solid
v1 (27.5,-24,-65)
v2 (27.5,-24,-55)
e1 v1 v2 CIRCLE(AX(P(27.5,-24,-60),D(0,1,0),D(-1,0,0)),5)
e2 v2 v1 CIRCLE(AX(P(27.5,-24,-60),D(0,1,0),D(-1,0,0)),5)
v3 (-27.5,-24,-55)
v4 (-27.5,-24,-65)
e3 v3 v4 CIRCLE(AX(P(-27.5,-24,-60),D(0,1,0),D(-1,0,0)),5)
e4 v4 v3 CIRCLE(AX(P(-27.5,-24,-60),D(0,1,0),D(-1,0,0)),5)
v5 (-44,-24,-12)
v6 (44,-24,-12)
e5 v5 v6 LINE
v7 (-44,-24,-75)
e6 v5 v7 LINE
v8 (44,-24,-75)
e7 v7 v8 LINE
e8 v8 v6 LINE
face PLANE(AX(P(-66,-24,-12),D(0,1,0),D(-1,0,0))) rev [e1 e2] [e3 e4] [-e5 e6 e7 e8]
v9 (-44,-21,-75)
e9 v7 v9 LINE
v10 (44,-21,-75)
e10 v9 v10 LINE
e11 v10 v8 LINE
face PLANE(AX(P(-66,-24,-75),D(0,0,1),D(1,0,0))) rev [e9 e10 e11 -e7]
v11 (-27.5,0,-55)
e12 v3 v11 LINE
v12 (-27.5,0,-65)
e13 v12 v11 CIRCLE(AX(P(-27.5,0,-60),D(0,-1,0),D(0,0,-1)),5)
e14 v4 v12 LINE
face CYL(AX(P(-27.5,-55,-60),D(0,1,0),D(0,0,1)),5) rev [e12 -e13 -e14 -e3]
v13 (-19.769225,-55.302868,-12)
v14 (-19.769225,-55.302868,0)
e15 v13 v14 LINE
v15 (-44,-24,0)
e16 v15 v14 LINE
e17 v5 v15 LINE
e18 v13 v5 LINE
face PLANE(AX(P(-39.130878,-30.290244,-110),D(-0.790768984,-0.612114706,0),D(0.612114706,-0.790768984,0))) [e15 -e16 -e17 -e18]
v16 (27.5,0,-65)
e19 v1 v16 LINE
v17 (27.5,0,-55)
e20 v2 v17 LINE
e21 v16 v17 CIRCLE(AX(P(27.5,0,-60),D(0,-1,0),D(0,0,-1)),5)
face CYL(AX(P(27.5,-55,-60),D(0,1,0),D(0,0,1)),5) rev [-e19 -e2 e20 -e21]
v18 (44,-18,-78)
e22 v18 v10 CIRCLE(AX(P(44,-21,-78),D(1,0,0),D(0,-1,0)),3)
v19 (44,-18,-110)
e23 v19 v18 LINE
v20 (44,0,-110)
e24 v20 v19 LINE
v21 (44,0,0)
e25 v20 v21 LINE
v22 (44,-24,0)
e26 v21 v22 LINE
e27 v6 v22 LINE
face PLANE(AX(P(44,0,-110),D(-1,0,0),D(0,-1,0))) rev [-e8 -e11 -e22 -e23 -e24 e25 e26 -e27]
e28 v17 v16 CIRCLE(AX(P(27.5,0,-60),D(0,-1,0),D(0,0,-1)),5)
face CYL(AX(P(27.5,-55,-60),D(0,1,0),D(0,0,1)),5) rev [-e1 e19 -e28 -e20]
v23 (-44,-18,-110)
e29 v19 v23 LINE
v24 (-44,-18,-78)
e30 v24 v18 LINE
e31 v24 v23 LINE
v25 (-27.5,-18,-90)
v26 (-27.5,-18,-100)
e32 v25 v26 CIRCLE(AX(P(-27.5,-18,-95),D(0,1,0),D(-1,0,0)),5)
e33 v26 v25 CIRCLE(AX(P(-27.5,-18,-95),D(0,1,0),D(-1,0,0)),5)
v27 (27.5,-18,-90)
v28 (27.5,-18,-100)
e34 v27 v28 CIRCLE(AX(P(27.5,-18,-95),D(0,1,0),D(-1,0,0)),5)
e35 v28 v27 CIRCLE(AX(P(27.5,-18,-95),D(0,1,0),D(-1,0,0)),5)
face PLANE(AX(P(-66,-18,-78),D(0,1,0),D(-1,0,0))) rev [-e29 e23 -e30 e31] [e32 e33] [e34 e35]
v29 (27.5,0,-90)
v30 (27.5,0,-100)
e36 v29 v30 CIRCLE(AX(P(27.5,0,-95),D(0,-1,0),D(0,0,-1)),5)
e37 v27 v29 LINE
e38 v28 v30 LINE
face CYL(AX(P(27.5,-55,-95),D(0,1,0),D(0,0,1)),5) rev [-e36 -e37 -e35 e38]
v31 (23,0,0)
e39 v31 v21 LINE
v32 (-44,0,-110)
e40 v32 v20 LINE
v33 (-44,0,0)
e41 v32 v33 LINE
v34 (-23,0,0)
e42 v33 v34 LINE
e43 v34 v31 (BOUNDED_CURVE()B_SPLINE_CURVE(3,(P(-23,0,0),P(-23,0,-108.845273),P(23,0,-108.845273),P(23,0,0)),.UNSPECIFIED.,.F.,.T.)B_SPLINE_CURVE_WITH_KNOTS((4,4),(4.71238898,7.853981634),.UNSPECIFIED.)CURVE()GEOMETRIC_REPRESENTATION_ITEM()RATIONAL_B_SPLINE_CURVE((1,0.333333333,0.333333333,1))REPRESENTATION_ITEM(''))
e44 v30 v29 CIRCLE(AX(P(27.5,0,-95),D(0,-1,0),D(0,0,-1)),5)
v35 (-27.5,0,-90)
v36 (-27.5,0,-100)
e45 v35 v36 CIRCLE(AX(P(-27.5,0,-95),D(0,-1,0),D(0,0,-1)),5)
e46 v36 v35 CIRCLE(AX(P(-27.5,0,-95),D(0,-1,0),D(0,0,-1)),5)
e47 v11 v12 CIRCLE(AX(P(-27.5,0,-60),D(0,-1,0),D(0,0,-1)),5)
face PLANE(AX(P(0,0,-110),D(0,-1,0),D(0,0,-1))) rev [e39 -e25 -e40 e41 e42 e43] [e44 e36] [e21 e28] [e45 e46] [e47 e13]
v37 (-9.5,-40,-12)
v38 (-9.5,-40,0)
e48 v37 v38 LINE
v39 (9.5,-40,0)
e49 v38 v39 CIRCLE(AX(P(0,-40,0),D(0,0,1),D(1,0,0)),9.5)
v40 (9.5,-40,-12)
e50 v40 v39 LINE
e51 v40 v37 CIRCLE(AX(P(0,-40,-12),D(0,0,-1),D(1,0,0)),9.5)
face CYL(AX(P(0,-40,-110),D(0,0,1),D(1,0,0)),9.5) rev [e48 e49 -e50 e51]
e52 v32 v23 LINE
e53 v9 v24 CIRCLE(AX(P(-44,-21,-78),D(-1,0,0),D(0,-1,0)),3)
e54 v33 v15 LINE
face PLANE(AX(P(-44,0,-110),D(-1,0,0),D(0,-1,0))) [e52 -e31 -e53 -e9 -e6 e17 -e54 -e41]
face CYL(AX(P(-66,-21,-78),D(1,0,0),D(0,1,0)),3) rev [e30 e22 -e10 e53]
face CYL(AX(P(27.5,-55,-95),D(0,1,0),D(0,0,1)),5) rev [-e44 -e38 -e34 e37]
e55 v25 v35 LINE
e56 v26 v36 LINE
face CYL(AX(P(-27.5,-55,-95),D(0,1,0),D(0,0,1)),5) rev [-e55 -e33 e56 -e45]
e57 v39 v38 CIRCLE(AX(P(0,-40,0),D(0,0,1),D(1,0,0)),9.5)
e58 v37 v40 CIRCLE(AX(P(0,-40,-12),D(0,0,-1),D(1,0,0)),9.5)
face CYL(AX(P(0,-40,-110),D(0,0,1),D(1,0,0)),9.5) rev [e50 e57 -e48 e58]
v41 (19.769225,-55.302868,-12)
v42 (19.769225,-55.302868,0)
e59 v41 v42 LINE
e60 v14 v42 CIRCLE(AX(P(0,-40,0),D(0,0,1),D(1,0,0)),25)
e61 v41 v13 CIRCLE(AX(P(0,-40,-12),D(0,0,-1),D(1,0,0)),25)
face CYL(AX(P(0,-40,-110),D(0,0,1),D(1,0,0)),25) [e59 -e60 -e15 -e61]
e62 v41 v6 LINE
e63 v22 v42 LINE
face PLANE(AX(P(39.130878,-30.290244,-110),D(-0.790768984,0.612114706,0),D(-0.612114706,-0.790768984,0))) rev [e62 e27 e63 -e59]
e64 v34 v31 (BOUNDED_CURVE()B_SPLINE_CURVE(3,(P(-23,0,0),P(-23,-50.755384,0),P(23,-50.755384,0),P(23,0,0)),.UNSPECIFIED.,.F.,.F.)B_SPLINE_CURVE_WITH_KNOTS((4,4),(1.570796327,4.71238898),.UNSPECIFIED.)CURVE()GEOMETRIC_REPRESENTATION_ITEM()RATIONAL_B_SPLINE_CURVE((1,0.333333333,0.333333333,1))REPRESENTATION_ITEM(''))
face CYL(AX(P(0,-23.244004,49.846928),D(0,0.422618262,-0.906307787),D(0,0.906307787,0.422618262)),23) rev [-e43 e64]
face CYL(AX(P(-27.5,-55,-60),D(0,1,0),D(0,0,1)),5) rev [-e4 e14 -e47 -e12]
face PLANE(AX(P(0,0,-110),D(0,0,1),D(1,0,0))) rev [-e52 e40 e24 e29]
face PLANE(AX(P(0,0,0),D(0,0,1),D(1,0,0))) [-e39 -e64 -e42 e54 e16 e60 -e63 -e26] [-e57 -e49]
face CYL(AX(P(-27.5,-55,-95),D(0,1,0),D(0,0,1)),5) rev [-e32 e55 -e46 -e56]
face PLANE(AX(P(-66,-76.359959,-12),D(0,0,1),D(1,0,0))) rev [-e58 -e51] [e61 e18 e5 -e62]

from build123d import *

# Parameters (mm, degrees)
BODY_PROFILE_SKETCH_R          = 25
BODY_PROFILE_SKETCH_R_2        = 9.5
BRACKET_BODY_EXTRUDE_110_DEPTH = 110
THROUGH_SLOT_CUT_DEPTH         = 110
ANGLED_BORE_SKETCH_46_R        = 23
ANGLED_BORE_46_DEPTH           = 55
MOUNTING_HOLES_SKETCH_R        = 5
MOUNTING_HOLES_4X_10_DEPTH     = 55


with BuildPart() as part:
    # Body Profile Sketch → Bracket Body Extrude 110 (new body)
    # profile 1 of 2: a face of its own
    with BuildSketch(Plane.XY):
        with BuildLine():
            Line((44, 0), (-44, 0))
            Line((-44, 0), (-44, -24))
            Line((-44, -24), (-19.769224603, -55.302867659))
            ThreePointArc((-19.769224603, -55.302867659), (-8.086080167, -16.343810376), (25, -40))
            ThreePointArc((25, -40), (23.656189624, -48.086080167), (19.769224603, -55.302867659))
            Line((19.769224603, -55.302867659), (44, -24))
            Line((44, -24), (44, 0))
        make_face()
    # profile 2 of 2: a face of its own
    with BuildSketch(Plane.XY):
        with Locations((0, -40)):
            Circle(BODY_PROFILE_SKETCH_R)
        with Locations((0, -40)):
            Circle(BODY_PROFILE_SKETCH_R_2, mode=Mode.SUBTRACT)
    extrude(amount=-BRACKET_BODY_EXTRUDE_110_DEPTH)

    # Through Slot Sketch → Through Slot Cut (cut)
    with BuildSketch(Plane(origin=(44, 0, 0), x_dir=(0, 0, -1), z_dir=(1, 0, 0))):
        with BuildLine():
            Line((12, -76.359959314), (12, -24))
            Line((12, -24), (75, -24))
            Line((75, -24), (75, -21))
            ThreePointArc((75, -21), (75.878679656, -18.878679656), (78, -18))
            Line((78, -18), (121.77138992, -18))
            Line((121.77138992, -18), (130.17802, -76.359959314))
            Line((130.17802, -76.359959314), (12, -76.359959314))
        make_face()
    extrude(amount=-THROUGH_SLOT_CUT_DEPTH, mode=Mode.SUBTRACT)

    # Angled Bore Sketch Ø46 → Angled Bore Ø46 (cut, symmetric)
    with BuildSketch(Plane(origin=(0, 0, 0), x_dir=(-1, 0, 0), z_dir=(0, 0.4226182617406939, -0.9063077870366526))):
        Circle(ANGLED_BORE_SKETCH_46_R)
    extrude(amount=ANGLED_BORE_46_DEPTH, both=True, mode=Mode.SUBTRACT)

    # Mounting Holes Sketch → Mounting Holes 4xØ10 (cut, symmetric)
    with BuildSketch(Plane(origin=(0, 0, 0), x_dir=(1, 0, 0), z_dir=(0, 1, 0))):
        with Locations(Location((-27.5, 95, 0), (0, 0, 180))):
            Circle(MOUNTING_HOLES_SKETCH_R)
        with Locations(Location((-27.5, 60, 0), (0, 0, 180))):
            Circle(MOUNTING_HOLES_SKETCH_R)
        with Locations(Location((27.5, 60, 0), (0, 0, 180))):
            Circle(MOUNTING_HOLES_SKETCH_R)
        with Locations(Location((27.5, 95, 0), (0, 0, 180))):
            Circle(MOUNTING_HOLES_SKETCH_R)
    extrude(amount=MOUNTING_HOLES_4X_10_DEPTH, both=True, mode=Mode.SUBTRACT)


solid = part.part
